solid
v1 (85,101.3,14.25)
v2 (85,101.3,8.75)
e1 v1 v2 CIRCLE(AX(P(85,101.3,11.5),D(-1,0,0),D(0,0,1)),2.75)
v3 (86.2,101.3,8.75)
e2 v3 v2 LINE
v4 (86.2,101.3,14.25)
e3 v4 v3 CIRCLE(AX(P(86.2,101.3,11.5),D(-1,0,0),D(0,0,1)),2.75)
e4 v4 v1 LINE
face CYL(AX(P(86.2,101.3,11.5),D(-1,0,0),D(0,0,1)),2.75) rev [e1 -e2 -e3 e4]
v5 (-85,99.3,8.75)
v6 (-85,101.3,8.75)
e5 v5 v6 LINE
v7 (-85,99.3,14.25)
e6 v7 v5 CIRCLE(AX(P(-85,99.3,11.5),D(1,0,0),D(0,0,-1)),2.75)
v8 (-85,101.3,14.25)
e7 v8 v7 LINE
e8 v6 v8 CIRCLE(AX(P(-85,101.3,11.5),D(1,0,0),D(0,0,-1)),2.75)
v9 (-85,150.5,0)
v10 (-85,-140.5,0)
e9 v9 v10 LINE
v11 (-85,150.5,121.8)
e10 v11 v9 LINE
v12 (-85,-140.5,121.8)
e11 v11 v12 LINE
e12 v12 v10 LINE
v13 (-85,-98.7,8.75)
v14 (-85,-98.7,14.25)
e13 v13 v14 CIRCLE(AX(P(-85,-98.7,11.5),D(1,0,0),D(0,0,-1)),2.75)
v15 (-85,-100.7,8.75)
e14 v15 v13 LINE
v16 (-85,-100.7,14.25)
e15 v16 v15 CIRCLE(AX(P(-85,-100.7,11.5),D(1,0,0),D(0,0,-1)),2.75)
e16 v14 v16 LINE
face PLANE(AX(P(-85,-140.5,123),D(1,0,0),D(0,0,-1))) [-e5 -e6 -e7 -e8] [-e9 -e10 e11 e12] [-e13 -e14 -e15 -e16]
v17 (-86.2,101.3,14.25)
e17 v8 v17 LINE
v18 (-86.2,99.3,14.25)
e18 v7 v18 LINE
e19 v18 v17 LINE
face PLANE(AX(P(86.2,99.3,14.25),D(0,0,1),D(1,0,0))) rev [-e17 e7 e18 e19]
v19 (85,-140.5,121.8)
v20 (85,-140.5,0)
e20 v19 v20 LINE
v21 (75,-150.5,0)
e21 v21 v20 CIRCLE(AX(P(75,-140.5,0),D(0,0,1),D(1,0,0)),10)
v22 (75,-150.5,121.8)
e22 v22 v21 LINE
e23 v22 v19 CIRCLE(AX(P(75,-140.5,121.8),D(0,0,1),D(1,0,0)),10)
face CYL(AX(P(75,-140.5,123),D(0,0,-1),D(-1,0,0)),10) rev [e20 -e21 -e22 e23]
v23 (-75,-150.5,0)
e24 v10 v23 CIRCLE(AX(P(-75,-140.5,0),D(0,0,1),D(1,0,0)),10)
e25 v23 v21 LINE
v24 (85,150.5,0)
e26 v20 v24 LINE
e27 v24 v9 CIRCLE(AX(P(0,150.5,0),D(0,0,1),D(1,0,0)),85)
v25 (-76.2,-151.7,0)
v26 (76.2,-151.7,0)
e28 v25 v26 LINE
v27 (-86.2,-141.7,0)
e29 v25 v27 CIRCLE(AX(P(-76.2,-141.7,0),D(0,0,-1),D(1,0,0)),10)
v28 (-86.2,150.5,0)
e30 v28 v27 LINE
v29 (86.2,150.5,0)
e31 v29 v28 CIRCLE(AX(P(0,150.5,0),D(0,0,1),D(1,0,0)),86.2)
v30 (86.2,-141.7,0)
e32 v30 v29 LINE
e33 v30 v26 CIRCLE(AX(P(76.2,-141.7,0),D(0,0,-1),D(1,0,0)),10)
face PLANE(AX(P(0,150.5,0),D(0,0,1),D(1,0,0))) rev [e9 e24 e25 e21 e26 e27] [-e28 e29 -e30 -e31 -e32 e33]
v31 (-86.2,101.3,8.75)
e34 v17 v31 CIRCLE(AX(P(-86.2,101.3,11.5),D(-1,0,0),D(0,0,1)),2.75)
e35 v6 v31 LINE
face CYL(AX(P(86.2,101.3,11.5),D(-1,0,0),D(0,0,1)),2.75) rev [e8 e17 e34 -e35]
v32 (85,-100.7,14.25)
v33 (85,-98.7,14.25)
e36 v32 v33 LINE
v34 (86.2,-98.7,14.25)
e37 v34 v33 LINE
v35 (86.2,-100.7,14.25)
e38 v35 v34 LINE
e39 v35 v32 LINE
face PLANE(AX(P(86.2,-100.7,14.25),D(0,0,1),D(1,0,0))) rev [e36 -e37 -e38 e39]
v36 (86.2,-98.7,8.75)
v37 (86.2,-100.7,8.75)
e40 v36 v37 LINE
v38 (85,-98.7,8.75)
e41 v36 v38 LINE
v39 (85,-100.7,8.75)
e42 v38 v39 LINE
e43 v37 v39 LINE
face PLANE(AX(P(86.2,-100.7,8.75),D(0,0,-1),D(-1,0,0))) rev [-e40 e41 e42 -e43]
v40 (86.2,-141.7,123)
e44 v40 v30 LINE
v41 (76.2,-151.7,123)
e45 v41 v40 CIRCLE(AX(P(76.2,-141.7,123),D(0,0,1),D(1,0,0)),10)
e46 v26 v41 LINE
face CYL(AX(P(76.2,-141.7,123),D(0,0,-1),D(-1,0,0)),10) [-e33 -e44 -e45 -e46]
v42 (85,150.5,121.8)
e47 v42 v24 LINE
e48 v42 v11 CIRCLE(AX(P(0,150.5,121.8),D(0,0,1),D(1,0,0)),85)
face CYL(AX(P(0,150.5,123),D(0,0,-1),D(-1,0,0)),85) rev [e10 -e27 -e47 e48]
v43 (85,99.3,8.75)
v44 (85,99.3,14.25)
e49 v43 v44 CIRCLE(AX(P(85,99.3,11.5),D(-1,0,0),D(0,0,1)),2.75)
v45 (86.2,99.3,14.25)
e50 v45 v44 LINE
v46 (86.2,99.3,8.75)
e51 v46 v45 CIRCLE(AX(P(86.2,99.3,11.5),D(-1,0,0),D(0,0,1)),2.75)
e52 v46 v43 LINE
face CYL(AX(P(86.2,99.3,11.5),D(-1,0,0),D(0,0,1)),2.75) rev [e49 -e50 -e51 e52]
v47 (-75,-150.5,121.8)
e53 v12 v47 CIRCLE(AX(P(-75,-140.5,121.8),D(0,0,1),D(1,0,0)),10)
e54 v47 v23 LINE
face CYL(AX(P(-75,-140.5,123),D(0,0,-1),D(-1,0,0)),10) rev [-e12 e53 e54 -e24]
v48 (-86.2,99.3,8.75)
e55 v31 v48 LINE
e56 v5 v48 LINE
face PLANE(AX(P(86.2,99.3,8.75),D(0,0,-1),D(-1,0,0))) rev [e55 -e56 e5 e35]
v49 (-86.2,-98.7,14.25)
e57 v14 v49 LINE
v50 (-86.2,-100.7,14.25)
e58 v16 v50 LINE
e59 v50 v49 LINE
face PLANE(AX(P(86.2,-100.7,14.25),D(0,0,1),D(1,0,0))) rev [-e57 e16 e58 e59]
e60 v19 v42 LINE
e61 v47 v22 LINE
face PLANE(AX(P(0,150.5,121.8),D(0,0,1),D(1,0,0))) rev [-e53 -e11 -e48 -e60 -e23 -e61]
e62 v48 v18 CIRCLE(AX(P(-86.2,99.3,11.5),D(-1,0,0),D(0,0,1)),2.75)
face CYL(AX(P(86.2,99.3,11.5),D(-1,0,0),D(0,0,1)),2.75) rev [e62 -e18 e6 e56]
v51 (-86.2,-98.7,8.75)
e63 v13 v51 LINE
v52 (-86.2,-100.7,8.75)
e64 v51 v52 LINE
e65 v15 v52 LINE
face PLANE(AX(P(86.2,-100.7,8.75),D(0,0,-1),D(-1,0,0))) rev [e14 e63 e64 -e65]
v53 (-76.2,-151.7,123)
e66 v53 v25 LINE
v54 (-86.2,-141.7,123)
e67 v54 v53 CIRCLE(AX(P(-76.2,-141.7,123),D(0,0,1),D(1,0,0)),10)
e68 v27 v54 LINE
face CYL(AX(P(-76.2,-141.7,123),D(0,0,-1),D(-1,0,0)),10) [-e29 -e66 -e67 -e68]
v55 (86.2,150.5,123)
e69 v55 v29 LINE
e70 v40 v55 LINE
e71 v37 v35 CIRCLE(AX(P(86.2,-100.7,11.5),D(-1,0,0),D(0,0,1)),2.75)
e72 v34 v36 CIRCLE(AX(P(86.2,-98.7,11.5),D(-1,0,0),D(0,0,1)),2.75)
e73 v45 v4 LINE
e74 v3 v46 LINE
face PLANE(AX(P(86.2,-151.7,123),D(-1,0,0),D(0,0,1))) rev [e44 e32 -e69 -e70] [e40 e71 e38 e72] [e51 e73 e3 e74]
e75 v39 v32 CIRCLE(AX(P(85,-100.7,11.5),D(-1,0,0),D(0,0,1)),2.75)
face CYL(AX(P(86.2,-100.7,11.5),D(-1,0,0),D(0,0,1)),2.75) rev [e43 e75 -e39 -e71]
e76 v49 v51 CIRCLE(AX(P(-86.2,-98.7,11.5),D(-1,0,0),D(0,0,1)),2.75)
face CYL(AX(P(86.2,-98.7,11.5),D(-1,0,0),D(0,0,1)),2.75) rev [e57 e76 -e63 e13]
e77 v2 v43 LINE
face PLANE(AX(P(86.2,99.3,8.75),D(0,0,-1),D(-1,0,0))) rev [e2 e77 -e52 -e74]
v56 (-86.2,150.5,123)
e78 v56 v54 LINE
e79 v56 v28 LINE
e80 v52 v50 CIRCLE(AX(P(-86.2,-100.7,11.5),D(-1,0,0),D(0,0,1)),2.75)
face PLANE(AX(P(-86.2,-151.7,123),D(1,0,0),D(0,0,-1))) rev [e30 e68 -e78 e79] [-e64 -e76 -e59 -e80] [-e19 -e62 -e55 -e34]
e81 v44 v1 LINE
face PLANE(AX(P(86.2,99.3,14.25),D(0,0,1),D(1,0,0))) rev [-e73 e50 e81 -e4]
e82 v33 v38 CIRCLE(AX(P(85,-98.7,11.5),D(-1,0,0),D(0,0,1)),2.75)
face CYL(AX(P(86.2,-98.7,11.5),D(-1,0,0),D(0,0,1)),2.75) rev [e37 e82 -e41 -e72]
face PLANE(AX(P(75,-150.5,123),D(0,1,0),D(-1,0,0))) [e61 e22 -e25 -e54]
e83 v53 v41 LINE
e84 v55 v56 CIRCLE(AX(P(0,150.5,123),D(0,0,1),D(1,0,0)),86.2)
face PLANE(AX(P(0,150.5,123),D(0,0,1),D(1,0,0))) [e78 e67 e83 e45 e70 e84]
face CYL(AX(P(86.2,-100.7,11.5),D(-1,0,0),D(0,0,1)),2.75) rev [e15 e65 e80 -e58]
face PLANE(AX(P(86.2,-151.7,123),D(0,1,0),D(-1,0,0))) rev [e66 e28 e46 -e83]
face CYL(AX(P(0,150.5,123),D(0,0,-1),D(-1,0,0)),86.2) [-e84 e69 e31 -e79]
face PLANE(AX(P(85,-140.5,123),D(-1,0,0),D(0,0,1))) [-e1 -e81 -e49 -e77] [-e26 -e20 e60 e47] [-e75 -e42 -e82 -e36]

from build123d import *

# Parameters (mm, degrees)
BOSS_EXTRUDE1_DEPTH = 123
BOSS_EXTRUDE2_START = -1.2
BOSS_EXTRUDE2_DEPTH = 1.2
FILLET1_R           = 10
FILLET2_R           = 10
CUT_EXTRUDE1_DEPTH  = 318.612421042


with BuildPart() as part:
    # Sketch1 → Boss-Extrude1 (new body)
    with BuildSketch(Plane.XY):
        with BuildLine():
            Line((-86.2, -151.7), (-86.2, 150.5))
            ThreePointArc((-86.2, 150.5), (0, 236.7), (86.2, 150.5))
            Line((86.2, 150.5), (86.2, -151.7))
            Line((86.2, -151.7), (-86.2, -151.7))
        make_face()
        with BuildLine():
            Line((75, -150.5), (-75, -150.5))
            ThreePointArc((-75, -150.5), (-82.071067812, -147.571067812), (-85, -140.5))
            Line((-85, -140.5), (-85, 150.5))
            ThreePointArc((-85, 150.5), (0, 235.5), (85, 150.5))
            Line((85, 150.5), (85, -140.5))
            ThreePointArc((85, -140.5), (82.071067812, -147.571067812), (75, -150.5))
        make_face(mode=Mode.SUBTRACT)
    extrude(amount=BOSS_EXTRUDE1_DEPTH)

    # Sketch2 → Boss-Extrude2 (add)
    with BuildSketch(Plane.XY.offset(123).offset(BOSS_EXTRUDE2_START)):
        with BuildLine():
            Line((-86.2, 150.5), (-86.2, -151.7))
            Line((-86.2, -151.7), (86.2, -151.7))
            Line((86.2, -151.7), (86.2, 150.5))
            ThreePointArc((86.2, 150.5), (0, 236.7), (-86.2, 150.5))
        make_face()
    extrude(amount=BOSS_EXTRUDE2_DEPTH)

    # Fillet1
    fillet1_edges = [part.edges().sort_by_distance(p)[0] for p in [
        (-86.2, -151.7, 61.5),
    ]]
    fillet(fillet1_edges, radius=FILLET1_R)

    # Fillet2
    fillet2_edges = [part.edges().sort_by_distance(p)[0] for p in [
        (86.2, -151.7, 61.5),
    ]]
    fillet(fillet2_edges, radius=FILLET2_R)

    # Sketch3 → Cut-Extrude1 (cut, through all)
    with BuildSketch(Plane.ZY.offset(86.2)):
        with BuildLine():
            Line((8.75, 99.3), (8.75, 101.3))
            ThreePointArc((8.75, 101.3), (11.5, 104.05), (14.25, 101.3))
            Line((14.25, 101.3), (14.25, 99.3))
            ThreePointArc((14.25, 99.3), (11.5, 96.55), (8.75, 99.3))
        make_face()
        with BuildLine():
            Line((8.75, -100.7), (8.75, -98.7))
            ThreePointArc((8.75, -98.7), (11.5, -95.95), (14.25, -98.7))
            Line((14.25, -98.7), (14.25, -100.7))
            ThreePointArc((14.25, -100.7), (11.5, -103.45), (8.75, -100.7))
        make_face()
    extrude(amount=-CUT_EXTRUDE1_DEPTH, mode=Mode.SUBTRACT)


solid = part.part
